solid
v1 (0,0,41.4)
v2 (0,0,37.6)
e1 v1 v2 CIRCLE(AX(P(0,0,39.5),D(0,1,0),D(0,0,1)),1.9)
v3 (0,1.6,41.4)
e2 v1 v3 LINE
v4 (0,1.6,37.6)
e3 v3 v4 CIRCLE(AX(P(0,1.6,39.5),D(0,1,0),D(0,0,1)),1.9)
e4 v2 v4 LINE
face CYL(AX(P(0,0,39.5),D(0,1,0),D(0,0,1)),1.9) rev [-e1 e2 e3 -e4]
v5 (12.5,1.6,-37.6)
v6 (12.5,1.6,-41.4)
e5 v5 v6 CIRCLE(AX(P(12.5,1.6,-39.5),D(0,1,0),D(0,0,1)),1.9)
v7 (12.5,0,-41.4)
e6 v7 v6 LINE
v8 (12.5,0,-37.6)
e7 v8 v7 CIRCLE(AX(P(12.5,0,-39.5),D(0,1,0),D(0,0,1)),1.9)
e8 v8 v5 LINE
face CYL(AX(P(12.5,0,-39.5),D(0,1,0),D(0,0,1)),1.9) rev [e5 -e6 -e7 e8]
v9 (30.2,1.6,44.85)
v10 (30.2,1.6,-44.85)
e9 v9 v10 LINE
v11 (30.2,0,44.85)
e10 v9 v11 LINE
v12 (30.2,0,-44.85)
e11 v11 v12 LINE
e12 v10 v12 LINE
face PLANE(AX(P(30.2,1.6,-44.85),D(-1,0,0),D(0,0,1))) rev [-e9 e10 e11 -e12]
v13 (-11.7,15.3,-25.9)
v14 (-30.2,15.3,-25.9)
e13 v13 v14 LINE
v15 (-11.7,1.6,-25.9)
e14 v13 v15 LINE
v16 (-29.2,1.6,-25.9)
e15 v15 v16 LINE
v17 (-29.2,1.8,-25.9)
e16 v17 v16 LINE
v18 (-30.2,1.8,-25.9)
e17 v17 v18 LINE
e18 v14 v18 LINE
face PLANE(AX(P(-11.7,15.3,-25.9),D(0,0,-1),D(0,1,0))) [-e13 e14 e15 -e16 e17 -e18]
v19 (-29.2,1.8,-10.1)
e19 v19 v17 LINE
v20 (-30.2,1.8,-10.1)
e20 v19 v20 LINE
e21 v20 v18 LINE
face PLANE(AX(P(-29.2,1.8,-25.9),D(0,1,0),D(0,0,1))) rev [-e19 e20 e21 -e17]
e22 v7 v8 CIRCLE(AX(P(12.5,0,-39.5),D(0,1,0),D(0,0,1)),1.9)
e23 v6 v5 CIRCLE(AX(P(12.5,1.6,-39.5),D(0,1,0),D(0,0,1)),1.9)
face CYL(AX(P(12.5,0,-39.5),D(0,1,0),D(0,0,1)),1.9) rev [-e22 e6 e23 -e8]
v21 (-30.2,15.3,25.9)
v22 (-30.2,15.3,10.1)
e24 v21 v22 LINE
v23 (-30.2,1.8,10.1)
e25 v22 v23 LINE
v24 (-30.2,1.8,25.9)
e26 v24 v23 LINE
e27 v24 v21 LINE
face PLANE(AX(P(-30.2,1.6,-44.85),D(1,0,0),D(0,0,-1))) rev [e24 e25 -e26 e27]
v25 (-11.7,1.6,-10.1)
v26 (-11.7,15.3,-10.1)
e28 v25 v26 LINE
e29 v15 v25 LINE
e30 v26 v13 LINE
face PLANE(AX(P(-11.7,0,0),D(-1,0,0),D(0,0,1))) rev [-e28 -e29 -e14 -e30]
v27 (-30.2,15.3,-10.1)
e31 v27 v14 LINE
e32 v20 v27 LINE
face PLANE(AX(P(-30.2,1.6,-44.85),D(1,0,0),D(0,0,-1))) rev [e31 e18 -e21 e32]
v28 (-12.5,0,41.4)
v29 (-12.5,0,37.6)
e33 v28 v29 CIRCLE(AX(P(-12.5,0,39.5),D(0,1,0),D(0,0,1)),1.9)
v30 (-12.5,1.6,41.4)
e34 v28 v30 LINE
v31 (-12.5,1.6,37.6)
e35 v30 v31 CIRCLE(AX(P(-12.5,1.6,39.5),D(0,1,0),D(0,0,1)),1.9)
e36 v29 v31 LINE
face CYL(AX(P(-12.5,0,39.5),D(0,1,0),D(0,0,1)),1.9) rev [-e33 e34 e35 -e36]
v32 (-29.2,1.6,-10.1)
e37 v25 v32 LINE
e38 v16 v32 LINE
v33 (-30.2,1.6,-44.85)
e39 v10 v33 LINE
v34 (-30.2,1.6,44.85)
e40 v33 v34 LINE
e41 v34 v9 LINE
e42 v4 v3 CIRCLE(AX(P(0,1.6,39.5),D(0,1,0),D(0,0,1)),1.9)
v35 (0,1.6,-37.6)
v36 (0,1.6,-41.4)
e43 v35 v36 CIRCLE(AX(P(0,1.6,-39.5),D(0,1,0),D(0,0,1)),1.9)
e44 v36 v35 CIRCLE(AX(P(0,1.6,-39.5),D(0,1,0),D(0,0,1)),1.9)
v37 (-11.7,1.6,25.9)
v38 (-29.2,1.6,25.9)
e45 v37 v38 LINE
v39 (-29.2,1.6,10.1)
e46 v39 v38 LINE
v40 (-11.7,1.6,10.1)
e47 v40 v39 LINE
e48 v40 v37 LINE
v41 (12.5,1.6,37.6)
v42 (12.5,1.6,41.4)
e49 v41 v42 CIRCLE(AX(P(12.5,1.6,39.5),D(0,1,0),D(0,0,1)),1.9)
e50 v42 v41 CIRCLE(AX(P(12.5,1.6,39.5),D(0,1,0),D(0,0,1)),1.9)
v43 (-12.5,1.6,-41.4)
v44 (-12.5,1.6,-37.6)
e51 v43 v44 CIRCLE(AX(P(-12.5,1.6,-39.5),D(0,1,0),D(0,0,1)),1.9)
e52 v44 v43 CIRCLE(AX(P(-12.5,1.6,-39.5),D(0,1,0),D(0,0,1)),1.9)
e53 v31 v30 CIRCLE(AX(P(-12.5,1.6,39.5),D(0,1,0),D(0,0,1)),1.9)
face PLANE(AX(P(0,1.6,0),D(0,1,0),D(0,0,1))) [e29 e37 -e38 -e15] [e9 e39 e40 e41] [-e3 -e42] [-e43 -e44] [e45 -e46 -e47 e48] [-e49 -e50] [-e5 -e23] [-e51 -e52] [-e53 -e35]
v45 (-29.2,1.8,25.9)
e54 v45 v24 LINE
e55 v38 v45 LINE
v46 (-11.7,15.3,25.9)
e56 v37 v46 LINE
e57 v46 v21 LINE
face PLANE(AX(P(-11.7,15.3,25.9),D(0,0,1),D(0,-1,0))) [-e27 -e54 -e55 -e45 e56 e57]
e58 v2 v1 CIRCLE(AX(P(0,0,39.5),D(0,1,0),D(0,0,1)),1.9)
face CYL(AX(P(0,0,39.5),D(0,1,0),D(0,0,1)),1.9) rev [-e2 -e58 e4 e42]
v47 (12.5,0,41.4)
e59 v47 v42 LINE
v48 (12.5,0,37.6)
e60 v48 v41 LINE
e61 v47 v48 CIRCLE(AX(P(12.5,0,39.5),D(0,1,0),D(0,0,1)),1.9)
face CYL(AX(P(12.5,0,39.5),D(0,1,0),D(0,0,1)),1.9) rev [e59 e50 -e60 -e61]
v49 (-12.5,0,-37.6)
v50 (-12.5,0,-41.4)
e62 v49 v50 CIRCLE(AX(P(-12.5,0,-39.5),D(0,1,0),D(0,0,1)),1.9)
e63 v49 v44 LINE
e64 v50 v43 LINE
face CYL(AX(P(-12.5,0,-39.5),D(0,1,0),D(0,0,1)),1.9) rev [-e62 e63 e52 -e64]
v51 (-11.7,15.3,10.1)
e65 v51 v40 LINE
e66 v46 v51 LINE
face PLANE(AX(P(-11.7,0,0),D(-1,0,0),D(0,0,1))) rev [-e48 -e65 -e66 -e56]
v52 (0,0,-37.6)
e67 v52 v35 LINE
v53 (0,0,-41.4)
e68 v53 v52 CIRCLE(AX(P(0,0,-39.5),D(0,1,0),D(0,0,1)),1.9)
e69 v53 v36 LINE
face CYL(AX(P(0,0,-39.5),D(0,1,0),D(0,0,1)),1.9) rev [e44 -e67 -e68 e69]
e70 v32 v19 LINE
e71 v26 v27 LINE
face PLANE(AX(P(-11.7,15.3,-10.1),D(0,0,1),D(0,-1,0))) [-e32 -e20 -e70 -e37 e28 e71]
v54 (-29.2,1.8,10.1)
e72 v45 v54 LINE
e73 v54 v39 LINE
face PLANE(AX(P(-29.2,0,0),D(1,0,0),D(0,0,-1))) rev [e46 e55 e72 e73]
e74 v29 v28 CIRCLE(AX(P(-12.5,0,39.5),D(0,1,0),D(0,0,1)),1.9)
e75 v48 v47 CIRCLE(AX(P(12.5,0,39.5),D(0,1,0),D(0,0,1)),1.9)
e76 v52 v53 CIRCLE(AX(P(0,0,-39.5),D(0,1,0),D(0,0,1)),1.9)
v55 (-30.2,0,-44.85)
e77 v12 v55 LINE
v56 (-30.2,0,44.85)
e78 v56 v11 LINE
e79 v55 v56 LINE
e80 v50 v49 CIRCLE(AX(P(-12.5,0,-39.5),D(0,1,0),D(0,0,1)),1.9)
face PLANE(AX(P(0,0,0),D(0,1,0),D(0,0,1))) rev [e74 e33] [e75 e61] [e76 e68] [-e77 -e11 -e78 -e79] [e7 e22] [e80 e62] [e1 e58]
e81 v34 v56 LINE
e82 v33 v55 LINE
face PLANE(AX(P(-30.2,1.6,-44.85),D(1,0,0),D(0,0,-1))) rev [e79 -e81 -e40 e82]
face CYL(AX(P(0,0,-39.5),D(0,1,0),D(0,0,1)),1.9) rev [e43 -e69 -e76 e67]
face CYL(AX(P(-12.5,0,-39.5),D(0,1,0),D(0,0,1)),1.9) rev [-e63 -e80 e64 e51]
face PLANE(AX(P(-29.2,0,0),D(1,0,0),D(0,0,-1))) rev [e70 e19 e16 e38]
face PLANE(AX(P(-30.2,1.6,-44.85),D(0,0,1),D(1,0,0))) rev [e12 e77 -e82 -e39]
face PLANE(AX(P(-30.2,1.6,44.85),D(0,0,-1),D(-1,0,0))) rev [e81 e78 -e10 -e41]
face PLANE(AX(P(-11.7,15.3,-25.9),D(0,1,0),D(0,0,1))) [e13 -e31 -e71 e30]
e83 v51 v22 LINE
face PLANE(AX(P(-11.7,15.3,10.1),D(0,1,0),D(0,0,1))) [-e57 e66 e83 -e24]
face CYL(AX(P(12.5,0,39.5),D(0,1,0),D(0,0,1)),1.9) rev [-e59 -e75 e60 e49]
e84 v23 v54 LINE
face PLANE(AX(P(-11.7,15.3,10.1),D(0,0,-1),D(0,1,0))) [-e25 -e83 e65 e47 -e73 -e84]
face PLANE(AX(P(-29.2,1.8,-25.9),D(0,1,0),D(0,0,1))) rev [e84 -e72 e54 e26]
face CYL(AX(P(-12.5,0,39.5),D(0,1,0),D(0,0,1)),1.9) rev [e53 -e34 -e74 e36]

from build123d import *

# Parameters (mm, degrees)
SKETCH_1_W          = 60.4
SKETCH_1_H          = 89.7
EXTRUDE_1_DEPTH     = 1.6
SKETCH_2_R          = 1.9
CUT_EXTRUDE_1_DEPTH = 1.6
SKETCH_3_W          = 15.8
SKETCH_3_H          = 13.7
EXTRUDE_2_DEPTH     = 18.5
SKETCH_4_W          = 51.8
SKETCH_4_H          = 0.2
CUT_EXTRUDE_2_DEPTH = 1


with BuildPart() as part:
    # 草图1 → 凸台-拉伸1 (new body)
    with BuildSketch(Plane(origin=(0, 0, 0), x_dir=(1, 0, 0), z_dir=(0, 1, 0))):
        Rectangle(SKETCH_1_W, SKETCH_1_H)
    extrude(amount=EXTRUDE_1_DEPTH)

    # 草图2 → 切除-拉伸1 (cut)
    with BuildSketch(Plane(origin=(0, 1.6, 0), x_dir=(1, 0, 0), z_dir=(0, 1, 0))):
        with Locations(Location((-12.5, -39.5, 0), (0, 0, 270))):
            Circle(SKETCH_2_R)
        with Locations(Location((12.5, -39.5, 0), (0, 0, 270))):
            Circle(SKETCH_2_R)
        with Locations(Location((-12.5, 39.5, 0), (0, 0, 270))):
            Circle(SKETCH_2_R)
        with Locations(Location((12.5, 39.5, 0), (0, 0, 270))):
            Circle(SKETCH_2_R)
        with Locations(Location((0, 39.5, 0), (0, 0, 270))):
            Circle(SKETCH_2_R)
        with Locations(Location((0, -39.5, 0), (0, 0, 270))):
            Circle(SKETCH_2_R)
    extrude(amount=-CUT_EXTRUDE_1_DEPTH, mode=Mode.SUBTRACT)

    # 草图3 → 凸台-拉伸2 (add)
    with BuildSketch(Plane.ZY.offset(30.2)):
        with Locations((18, 8.45)):
            Rectangle(SKETCH_3_W, SKETCH_3_H)
        with Locations((-18, 8.45)):
            Rectangle(SKETCH_3_W, SKETCH_3_H)
    extrude(amount=-EXTRUDE_2_DEPTH)

    # 草图4 → 切除-拉伸2 (cut)
    with BuildSketch(Plane.ZY.offset(30.2)):
        with Locations((0, 1.7)):
            Rectangle(SKETCH_4_W, SKETCH_4_H)
    extrude(amount=-CUT_EXTRUDE_2_DEPTH, mode=Mode.SUBTRACT)


solid = part.part
